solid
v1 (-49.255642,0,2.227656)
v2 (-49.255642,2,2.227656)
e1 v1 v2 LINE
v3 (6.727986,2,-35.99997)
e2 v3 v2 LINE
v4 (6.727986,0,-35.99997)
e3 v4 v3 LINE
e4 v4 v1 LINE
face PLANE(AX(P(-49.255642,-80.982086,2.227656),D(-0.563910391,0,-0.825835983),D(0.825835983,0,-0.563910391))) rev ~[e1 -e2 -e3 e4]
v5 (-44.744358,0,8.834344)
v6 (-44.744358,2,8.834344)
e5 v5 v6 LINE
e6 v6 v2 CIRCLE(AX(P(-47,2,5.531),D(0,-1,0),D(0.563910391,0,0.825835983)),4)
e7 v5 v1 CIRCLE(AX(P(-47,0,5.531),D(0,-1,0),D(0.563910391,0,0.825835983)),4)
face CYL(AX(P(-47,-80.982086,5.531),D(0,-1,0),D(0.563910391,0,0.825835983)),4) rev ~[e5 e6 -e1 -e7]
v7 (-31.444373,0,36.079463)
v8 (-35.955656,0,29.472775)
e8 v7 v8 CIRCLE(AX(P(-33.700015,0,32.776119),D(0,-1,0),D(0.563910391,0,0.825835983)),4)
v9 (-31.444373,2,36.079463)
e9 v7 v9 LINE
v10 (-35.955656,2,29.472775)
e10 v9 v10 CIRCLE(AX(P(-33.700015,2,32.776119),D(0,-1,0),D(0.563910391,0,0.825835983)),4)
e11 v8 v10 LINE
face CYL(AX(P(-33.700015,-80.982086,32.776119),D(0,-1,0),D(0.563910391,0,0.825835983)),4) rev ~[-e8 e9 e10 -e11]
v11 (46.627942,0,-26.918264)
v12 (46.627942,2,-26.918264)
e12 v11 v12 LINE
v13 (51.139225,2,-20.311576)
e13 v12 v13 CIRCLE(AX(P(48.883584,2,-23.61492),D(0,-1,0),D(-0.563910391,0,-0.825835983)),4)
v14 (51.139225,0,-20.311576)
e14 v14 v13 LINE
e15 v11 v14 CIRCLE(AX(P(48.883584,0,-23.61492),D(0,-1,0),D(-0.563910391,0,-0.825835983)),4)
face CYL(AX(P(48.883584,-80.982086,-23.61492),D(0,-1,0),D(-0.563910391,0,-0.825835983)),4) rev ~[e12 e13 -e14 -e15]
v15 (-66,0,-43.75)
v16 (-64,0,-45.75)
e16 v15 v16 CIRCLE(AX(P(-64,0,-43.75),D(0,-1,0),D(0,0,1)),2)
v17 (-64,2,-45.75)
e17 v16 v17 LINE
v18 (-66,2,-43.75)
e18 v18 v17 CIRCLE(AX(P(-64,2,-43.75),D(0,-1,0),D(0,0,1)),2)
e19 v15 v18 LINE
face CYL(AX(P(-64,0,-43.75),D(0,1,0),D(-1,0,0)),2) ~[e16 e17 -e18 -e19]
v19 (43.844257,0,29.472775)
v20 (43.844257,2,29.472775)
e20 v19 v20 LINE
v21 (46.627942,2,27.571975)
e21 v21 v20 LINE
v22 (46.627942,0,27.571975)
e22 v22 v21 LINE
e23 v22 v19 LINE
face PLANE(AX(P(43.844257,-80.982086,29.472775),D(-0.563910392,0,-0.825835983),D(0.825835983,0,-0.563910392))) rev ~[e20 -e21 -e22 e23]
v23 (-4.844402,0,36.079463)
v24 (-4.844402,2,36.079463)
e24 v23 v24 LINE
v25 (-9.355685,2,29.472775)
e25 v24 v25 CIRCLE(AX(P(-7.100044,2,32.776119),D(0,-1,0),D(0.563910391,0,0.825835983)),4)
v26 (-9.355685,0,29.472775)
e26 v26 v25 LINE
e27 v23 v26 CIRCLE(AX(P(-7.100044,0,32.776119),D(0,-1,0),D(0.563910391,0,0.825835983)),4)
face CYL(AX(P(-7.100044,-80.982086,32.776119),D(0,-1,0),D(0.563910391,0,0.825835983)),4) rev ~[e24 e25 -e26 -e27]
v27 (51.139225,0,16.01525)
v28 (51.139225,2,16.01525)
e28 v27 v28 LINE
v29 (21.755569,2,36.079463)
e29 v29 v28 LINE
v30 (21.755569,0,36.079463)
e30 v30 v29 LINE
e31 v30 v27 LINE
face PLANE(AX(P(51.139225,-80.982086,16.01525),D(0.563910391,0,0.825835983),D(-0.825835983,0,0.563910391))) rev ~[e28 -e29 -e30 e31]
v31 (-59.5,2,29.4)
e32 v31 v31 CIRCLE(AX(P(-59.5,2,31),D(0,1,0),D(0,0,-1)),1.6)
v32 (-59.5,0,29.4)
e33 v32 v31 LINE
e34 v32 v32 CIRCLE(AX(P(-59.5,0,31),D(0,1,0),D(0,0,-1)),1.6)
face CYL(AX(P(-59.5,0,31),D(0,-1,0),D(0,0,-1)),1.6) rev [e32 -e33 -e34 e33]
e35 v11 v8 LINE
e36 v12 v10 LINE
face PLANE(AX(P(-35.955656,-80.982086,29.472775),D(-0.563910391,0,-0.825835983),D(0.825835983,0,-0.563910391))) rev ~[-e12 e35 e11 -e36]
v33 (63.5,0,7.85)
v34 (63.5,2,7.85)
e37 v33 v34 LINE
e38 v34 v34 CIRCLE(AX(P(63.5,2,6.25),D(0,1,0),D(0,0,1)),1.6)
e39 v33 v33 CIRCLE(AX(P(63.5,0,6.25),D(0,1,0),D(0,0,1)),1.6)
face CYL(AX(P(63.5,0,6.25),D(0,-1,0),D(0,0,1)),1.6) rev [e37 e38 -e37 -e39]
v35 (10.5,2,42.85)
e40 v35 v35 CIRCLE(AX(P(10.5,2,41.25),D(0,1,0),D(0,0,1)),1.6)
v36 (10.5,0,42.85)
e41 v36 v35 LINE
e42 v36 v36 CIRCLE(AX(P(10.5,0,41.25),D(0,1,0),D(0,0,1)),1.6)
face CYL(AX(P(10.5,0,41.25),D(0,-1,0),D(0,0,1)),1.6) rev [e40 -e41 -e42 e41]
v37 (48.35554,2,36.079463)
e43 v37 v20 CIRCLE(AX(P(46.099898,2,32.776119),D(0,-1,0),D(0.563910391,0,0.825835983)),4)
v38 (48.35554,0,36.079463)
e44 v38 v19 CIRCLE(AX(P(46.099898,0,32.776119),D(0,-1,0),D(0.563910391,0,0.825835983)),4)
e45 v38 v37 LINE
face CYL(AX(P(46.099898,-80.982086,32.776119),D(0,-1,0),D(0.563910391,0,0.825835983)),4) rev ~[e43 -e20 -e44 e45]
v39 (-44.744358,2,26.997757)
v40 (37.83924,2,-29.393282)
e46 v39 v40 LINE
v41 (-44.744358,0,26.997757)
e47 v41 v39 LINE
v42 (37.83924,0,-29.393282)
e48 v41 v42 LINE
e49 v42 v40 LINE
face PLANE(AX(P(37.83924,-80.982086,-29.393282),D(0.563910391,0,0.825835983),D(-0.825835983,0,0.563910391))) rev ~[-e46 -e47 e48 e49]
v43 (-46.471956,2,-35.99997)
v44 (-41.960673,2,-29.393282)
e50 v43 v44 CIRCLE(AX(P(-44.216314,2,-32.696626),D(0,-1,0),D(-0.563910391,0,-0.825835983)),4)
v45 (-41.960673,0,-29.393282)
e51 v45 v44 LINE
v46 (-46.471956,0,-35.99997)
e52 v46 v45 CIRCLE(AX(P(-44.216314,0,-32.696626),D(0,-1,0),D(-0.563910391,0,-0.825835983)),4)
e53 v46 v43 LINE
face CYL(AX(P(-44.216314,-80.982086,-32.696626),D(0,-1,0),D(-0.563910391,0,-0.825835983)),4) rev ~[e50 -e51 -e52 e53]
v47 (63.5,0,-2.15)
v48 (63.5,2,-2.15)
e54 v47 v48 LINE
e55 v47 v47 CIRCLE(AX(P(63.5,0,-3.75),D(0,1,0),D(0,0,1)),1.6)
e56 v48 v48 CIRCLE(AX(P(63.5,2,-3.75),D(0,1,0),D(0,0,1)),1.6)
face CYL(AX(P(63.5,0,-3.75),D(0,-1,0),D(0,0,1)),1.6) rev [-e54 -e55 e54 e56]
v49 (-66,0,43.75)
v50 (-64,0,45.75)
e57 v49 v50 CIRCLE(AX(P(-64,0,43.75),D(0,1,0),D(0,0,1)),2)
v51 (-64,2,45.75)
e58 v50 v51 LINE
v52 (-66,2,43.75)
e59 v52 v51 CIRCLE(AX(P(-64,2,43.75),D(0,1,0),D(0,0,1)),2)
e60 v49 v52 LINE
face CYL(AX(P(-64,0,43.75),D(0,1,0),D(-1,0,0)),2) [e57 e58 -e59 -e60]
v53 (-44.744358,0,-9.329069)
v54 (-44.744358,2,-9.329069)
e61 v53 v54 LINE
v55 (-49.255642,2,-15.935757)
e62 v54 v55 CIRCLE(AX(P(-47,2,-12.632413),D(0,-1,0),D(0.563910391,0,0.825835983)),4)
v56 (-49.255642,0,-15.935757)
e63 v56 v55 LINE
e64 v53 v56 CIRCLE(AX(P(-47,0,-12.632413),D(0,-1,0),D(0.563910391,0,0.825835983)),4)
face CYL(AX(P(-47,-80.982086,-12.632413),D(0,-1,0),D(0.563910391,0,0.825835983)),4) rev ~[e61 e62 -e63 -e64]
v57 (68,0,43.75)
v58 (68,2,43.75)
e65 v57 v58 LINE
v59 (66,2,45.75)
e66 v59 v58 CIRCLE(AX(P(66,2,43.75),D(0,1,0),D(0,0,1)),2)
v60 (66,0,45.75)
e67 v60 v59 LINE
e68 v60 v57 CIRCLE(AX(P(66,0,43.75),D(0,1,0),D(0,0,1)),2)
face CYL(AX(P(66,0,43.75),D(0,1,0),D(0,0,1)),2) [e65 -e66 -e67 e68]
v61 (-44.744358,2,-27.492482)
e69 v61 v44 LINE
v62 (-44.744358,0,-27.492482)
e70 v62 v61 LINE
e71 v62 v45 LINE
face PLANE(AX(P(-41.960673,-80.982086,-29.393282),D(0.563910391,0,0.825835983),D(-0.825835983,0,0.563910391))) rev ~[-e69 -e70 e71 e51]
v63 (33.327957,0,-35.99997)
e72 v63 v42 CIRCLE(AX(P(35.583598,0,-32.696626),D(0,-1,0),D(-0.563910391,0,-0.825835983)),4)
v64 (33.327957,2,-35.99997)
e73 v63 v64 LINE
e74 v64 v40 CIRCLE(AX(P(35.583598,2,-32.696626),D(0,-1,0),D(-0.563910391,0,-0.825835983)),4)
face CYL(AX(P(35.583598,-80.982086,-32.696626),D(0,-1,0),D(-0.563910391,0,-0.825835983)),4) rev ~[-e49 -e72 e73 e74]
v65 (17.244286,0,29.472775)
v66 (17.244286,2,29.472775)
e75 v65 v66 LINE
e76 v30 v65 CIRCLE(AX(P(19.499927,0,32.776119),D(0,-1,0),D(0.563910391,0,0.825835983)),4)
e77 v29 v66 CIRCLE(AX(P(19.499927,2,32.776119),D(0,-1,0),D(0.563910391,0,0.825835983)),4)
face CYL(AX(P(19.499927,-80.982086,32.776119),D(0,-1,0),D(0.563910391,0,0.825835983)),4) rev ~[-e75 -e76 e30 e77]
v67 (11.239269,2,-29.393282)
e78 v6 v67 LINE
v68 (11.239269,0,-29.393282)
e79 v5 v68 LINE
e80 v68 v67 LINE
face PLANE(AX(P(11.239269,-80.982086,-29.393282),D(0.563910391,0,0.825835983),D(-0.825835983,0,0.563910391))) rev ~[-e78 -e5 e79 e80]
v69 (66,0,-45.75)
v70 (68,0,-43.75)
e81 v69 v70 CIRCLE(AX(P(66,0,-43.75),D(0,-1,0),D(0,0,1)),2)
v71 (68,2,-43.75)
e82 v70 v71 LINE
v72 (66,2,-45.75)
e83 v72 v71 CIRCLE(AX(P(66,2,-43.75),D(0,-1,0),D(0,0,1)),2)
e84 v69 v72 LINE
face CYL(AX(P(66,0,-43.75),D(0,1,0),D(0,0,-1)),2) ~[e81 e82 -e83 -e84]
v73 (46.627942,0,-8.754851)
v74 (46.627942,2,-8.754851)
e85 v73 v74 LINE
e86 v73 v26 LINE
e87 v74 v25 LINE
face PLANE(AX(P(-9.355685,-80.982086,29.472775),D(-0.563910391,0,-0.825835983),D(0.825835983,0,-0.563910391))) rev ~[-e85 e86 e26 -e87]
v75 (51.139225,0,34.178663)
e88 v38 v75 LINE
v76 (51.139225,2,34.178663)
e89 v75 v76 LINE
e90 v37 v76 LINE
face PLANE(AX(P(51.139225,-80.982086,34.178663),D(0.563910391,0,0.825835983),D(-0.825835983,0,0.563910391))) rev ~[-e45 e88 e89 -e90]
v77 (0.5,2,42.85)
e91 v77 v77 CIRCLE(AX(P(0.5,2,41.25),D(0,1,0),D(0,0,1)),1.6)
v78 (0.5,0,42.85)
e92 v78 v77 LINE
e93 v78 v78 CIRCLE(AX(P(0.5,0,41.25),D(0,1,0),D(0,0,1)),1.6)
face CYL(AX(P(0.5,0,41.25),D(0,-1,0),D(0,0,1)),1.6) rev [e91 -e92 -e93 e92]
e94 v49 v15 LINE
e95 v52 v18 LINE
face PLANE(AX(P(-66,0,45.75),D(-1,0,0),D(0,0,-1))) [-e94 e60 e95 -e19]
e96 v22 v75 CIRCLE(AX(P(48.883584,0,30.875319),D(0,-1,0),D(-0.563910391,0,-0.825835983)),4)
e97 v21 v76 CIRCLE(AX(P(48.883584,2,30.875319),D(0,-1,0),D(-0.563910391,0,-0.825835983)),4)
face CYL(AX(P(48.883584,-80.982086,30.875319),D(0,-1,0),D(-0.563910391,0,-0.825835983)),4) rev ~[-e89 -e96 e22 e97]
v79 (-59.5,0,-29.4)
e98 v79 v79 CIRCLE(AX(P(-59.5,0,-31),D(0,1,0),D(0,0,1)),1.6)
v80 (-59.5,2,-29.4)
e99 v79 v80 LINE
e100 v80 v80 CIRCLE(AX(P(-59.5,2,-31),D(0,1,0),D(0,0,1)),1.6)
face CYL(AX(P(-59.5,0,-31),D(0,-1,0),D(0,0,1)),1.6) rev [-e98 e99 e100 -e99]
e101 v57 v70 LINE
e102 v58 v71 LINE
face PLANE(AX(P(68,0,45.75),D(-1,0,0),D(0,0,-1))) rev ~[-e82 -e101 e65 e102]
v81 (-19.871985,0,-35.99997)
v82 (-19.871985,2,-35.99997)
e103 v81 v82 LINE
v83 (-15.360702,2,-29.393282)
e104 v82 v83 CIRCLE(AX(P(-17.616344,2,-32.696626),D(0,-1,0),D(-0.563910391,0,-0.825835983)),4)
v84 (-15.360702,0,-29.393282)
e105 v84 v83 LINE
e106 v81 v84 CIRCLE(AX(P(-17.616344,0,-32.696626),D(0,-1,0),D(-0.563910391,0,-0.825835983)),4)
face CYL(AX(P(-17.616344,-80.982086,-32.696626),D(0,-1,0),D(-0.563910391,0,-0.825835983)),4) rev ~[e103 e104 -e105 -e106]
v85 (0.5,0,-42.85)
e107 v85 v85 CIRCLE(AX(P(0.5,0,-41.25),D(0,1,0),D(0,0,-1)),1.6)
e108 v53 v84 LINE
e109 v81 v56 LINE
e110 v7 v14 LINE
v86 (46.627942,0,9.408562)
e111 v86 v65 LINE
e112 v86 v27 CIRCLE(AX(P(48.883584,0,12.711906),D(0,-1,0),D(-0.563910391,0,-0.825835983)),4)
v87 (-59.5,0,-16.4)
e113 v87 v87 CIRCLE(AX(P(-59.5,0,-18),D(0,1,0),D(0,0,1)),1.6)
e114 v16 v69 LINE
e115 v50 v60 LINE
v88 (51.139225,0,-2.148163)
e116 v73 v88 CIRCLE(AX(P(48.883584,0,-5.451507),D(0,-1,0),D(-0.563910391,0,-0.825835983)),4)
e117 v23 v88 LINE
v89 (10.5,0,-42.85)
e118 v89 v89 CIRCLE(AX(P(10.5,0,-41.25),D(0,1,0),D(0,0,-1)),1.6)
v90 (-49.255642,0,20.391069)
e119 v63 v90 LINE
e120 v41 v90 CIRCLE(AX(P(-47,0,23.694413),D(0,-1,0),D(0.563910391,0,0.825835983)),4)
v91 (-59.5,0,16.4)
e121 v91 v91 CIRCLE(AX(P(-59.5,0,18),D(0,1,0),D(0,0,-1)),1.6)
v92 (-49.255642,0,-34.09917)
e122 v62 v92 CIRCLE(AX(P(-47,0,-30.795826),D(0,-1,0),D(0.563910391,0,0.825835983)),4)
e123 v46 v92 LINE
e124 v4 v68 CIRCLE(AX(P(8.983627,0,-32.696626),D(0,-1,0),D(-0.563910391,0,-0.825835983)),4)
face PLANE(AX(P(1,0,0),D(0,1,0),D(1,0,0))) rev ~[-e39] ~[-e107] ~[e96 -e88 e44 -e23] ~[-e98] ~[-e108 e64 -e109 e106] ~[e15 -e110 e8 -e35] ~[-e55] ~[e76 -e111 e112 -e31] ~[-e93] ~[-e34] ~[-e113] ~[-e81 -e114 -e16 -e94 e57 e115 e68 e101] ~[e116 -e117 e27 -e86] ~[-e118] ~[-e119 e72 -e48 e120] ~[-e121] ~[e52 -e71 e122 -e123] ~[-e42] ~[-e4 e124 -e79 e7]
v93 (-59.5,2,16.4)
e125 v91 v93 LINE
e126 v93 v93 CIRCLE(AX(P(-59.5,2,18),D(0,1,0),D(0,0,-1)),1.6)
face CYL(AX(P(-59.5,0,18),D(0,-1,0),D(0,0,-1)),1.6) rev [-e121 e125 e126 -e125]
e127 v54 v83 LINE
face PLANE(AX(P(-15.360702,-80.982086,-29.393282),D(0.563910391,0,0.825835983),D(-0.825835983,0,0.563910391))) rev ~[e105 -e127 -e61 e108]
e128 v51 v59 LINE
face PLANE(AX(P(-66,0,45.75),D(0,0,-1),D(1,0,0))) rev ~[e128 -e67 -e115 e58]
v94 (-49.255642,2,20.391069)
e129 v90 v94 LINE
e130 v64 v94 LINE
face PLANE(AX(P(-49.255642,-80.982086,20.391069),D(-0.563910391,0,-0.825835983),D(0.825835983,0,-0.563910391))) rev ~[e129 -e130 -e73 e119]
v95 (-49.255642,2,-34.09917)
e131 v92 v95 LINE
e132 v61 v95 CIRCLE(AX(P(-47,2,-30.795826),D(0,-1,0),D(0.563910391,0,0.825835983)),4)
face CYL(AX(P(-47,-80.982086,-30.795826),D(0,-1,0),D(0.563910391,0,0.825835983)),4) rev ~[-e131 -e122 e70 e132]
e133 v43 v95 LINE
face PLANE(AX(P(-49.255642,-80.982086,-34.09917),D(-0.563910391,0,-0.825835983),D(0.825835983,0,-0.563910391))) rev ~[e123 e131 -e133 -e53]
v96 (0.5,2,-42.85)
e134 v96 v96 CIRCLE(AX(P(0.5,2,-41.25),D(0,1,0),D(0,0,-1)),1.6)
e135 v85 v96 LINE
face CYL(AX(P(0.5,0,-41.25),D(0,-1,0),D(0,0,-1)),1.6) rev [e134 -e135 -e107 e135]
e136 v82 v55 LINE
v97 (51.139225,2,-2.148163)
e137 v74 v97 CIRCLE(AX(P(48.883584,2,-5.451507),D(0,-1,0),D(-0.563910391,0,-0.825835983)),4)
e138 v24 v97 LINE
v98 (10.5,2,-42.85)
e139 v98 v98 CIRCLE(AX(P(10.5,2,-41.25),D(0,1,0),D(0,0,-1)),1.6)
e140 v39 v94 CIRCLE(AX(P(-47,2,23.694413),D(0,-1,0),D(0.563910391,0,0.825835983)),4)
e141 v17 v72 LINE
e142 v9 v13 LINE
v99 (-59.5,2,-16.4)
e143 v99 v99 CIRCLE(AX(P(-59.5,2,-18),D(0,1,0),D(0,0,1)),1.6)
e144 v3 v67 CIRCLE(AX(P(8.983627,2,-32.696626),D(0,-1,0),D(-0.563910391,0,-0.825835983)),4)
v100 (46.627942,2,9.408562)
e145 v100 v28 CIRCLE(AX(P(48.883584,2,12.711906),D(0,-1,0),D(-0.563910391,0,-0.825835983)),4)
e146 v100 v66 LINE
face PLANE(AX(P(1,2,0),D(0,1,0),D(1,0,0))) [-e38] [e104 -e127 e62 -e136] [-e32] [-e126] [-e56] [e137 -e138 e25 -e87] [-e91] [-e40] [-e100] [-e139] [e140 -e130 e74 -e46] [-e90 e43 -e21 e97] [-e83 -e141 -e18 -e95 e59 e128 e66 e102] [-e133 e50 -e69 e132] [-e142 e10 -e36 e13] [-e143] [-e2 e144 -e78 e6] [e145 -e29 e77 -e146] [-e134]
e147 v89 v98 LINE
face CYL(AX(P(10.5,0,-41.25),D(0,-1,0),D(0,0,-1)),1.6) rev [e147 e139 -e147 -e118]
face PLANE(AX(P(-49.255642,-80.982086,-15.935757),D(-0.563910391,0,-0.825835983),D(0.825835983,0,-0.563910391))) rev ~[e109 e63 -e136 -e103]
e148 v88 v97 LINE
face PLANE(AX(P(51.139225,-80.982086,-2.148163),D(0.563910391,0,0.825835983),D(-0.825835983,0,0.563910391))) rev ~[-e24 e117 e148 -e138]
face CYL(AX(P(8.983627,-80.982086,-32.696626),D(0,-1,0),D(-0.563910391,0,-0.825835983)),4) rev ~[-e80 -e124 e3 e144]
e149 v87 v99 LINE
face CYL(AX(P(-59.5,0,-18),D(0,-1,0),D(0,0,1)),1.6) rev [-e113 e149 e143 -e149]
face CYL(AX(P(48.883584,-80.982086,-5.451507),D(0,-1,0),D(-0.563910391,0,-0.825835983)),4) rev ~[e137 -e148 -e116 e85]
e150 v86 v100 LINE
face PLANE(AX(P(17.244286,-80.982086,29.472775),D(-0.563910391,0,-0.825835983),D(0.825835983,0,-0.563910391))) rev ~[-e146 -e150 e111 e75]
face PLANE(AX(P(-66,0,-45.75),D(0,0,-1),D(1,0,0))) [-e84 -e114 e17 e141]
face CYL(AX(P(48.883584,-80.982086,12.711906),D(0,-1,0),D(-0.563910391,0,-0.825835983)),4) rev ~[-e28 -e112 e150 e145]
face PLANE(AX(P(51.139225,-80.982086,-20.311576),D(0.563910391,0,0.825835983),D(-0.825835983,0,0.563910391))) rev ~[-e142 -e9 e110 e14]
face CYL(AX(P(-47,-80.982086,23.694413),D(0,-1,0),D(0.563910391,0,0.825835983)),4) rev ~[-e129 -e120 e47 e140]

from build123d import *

# Parameters (mm, degrees)
SKETCH1_W               = 134
SKETCH1_H               = 91.5
SKETCH1_R               = 1.6
BOSS_EXTRUDE1_DEPTH     = 2
CUT_EXTRUDE2_DEPTH      = 82.982086458
CUT_EXTRUDE2_DEPTH_BACK = 82.982086458
R2_FILLET_1_R           = 2


with BuildPart() as part:
    # Sketch1 → Boss-Extrude1 (new body)
    with BuildSketch(Plane(origin=(0, 0, 0), x_dir=(1, 0, 0), z_dir=(0, 1, 0))):
        with Locations((1, 0)):
            Rectangle(SKETCH1_W, SKETCH1_H)
        with Locations(Location((-59.5, 31, 0), (0, 0, 270))):
            Circle(SKETCH1_R, mode=Mode.SUBTRACT)
        with Locations(Location((-59.5, 18, 0), (0, 0, 270))):
            Circle(SKETCH1_R, mode=Mode.SUBTRACT)
        with Locations(Location((-59.5, -18, 0), (0, 0, 90))):
            Circle(SKETCH1_R, mode=Mode.SUBTRACT)
        with Locations(Location((-59.5, -31, 0), (0, 0, 90))):
            Circle(SKETCH1_R, mode=Mode.SUBTRACT)
        with Locations(Location((63.5, 3.75, 0), (0, 0, 270))):
            Circle(SKETCH1_R, mode=Mode.SUBTRACT)
        with Locations(Location((63.5, -6.25, 0), (0, 0, 270))):
            Circle(SKETCH1_R, mode=Mode.SUBTRACT)
        with Locations(Location((0.5, -41.25, 0), (0, 0, 270))):
            Circle(SKETCH1_R, mode=Mode.SUBTRACT)
        with Locations(Location((10.5, -41.25, 0), (0, 0, 270))):
            Circle(SKETCH1_R, mode=Mode.SUBTRACT)
        with Locations(Location((10.5, 41.25, 0), (0, 0, 90))):
            Circle(SKETCH1_R, mode=Mode.SUBTRACT)
        with Locations(Location((0.5, 41.25, 0), (0, 0, 90))):
            Circle(SKETCH1_R, mode=Mode.SUBTRACT)
    extrude(amount=BOSS_EXTRUDE1_DEPTH)

    # Sketch5 → Cut-Extrude2 (cut, two sides: drawn at the far end of the back side and taken through both)
    with BuildSketch(Plane(origin=(0, 2, 0), x_dir=(1, 0, 0), z_dir=(0, 1, 0)).offset(-CUT_EXTRUDE2_DEPTH_BACK)):
        with BuildLine():
            Line((-49.255641565, 34.099169914), (-46.471955987, 35.999970141))
            ThreePointArc((-46.471955987, 35.999970141), (-40.91297049, 34.952267774), (-41.960672856, 29.393282278))
            Line((-41.960672856, 29.393282278), (-44.744358435, 27.492482051))
            ThreePointArc((-44.744358435, 27.492482051), (-50.303343931, 28.540184417), (-49.255641565, 34.099169914))
        make_face()
        with BuildLine():
            Line((-49.255641565, 15.935756946), (-19.871985084, 35.999970141))
            ThreePointArc((-19.871985084, 35.999970141), (-14.312999587, 34.952267774), (-15.360701954, 29.393282278))
            Line((-15.360701954, 29.393282278), (-44.744358435, 9.329069084))
            ThreePointArc((-44.744358435, 9.329069084), (-50.303343931, 10.37677145), (-49.255641565, 15.935756946))
        make_face()
        with BuildLine():
            Line((-49.255641565, -2.227656021), (6.727985819, 35.999970141))
            ThreePointArc((6.727985819, 35.999970141), (12.286971315, 34.952267774), (11.239268949, 29.393282278))
            Line((11.239268949, 29.393282278), (-44.744358435, -8.834343884))
            ThreePointArc((-44.744358435, -8.834343884), (-50.303343931, -7.786641517), (-49.255641565, -2.227656021))
        make_face()
        with BuildLine():
            Line((-49.255641565, -20.391068988), (33.327956722, 35.999970141))
            ThreePointArc((33.327956722, 35.999970141), (38.886942218, 34.952267774), (37.839239852, 29.393282278))
            Line((37.839239852, 29.393282278), (-44.744358435, -26.997756851))
            ThreePointArc((-44.744358435, -26.997756851), (-50.303343931, -25.950054485), (-49.255641565, -20.391068988))
        make_face()
        with BuildLine():
            Line((-35.955656114, -29.472775472), (46.627942173, 26.918263657))
            ThreePointArc((46.627942173, 26.918263657), (52.18692767, 25.870561291), (51.139225303, 20.311575794))
            Line((51.139225303, 20.311575794), (-31.444372983, -36.079463334))
            ThreePointArc((-31.444372983, -36.079463334), (-37.00335848, -35.031760968), (-35.955656114, -29.472775472))
        make_face()
        with BuildLine():
            Line((-9.355685211, -29.472775472), (46.627942173, 8.75485069))
            ThreePointArc((46.627942173, 8.75485069), (52.18692767, 7.707148324), (51.139225303, 2.148162827))
            Line((51.139225303, 2.148162827), (-4.844402081, -36.079463334))
            ThreePointArc((-4.844402081, -36.079463334), (-10.403387577, -35.031760968), (-9.355685211, -29.472775472))
        make_face()
        with BuildLine():
            Line((17.244285692, -29.472775472), (46.627942173, -9.408562277))
            ThreePointArc((46.627942173, -9.408562277), (52.18692767, -10.456264644), (51.139225303, -16.01525014))
            Line((51.139225303, -16.01525014), (21.755568822, -36.079463334))
            ThreePointArc((21.755568822, -36.079463334), (16.196583325, -35.031760968), (17.244285692, -29.472775472))
        make_face()
        with BuildLine():
            Line((43.844256595, -29.472775472), (46.627942173, -27.571975244))
            ThreePointArc((46.627942173, -27.571975244), (52.18692767, -28.619677611), (51.139225303, -34.178663107))
            Line((51.139225303, -34.178663107), (48.355539725, -36.079463334))
            ThreePointArc((48.355539725, -36.079463334), (42.796554228, -35.031760968), (43.844256595, -29.472775472))
        make_face()
    extrude(amount=CUT_EXTRUDE2_DEPTH + CUT_EXTRUDE2_DEPTH_BACK, mode=Mode.SUBTRACT)

    # R2 Fillet 1
    r2_fillet_1_edges = [part.edges().sort_by_distance(p)[0] for p in [
        (-66, 1, -45.75),
        (68, 1, -45.75),
        (68, 1, 45.75),
        (-66, 1, 45.75),
    ]]
    fillet(r2_fillet_1_edges, radius=R2_FILLET_1_R)


solid = part.part
